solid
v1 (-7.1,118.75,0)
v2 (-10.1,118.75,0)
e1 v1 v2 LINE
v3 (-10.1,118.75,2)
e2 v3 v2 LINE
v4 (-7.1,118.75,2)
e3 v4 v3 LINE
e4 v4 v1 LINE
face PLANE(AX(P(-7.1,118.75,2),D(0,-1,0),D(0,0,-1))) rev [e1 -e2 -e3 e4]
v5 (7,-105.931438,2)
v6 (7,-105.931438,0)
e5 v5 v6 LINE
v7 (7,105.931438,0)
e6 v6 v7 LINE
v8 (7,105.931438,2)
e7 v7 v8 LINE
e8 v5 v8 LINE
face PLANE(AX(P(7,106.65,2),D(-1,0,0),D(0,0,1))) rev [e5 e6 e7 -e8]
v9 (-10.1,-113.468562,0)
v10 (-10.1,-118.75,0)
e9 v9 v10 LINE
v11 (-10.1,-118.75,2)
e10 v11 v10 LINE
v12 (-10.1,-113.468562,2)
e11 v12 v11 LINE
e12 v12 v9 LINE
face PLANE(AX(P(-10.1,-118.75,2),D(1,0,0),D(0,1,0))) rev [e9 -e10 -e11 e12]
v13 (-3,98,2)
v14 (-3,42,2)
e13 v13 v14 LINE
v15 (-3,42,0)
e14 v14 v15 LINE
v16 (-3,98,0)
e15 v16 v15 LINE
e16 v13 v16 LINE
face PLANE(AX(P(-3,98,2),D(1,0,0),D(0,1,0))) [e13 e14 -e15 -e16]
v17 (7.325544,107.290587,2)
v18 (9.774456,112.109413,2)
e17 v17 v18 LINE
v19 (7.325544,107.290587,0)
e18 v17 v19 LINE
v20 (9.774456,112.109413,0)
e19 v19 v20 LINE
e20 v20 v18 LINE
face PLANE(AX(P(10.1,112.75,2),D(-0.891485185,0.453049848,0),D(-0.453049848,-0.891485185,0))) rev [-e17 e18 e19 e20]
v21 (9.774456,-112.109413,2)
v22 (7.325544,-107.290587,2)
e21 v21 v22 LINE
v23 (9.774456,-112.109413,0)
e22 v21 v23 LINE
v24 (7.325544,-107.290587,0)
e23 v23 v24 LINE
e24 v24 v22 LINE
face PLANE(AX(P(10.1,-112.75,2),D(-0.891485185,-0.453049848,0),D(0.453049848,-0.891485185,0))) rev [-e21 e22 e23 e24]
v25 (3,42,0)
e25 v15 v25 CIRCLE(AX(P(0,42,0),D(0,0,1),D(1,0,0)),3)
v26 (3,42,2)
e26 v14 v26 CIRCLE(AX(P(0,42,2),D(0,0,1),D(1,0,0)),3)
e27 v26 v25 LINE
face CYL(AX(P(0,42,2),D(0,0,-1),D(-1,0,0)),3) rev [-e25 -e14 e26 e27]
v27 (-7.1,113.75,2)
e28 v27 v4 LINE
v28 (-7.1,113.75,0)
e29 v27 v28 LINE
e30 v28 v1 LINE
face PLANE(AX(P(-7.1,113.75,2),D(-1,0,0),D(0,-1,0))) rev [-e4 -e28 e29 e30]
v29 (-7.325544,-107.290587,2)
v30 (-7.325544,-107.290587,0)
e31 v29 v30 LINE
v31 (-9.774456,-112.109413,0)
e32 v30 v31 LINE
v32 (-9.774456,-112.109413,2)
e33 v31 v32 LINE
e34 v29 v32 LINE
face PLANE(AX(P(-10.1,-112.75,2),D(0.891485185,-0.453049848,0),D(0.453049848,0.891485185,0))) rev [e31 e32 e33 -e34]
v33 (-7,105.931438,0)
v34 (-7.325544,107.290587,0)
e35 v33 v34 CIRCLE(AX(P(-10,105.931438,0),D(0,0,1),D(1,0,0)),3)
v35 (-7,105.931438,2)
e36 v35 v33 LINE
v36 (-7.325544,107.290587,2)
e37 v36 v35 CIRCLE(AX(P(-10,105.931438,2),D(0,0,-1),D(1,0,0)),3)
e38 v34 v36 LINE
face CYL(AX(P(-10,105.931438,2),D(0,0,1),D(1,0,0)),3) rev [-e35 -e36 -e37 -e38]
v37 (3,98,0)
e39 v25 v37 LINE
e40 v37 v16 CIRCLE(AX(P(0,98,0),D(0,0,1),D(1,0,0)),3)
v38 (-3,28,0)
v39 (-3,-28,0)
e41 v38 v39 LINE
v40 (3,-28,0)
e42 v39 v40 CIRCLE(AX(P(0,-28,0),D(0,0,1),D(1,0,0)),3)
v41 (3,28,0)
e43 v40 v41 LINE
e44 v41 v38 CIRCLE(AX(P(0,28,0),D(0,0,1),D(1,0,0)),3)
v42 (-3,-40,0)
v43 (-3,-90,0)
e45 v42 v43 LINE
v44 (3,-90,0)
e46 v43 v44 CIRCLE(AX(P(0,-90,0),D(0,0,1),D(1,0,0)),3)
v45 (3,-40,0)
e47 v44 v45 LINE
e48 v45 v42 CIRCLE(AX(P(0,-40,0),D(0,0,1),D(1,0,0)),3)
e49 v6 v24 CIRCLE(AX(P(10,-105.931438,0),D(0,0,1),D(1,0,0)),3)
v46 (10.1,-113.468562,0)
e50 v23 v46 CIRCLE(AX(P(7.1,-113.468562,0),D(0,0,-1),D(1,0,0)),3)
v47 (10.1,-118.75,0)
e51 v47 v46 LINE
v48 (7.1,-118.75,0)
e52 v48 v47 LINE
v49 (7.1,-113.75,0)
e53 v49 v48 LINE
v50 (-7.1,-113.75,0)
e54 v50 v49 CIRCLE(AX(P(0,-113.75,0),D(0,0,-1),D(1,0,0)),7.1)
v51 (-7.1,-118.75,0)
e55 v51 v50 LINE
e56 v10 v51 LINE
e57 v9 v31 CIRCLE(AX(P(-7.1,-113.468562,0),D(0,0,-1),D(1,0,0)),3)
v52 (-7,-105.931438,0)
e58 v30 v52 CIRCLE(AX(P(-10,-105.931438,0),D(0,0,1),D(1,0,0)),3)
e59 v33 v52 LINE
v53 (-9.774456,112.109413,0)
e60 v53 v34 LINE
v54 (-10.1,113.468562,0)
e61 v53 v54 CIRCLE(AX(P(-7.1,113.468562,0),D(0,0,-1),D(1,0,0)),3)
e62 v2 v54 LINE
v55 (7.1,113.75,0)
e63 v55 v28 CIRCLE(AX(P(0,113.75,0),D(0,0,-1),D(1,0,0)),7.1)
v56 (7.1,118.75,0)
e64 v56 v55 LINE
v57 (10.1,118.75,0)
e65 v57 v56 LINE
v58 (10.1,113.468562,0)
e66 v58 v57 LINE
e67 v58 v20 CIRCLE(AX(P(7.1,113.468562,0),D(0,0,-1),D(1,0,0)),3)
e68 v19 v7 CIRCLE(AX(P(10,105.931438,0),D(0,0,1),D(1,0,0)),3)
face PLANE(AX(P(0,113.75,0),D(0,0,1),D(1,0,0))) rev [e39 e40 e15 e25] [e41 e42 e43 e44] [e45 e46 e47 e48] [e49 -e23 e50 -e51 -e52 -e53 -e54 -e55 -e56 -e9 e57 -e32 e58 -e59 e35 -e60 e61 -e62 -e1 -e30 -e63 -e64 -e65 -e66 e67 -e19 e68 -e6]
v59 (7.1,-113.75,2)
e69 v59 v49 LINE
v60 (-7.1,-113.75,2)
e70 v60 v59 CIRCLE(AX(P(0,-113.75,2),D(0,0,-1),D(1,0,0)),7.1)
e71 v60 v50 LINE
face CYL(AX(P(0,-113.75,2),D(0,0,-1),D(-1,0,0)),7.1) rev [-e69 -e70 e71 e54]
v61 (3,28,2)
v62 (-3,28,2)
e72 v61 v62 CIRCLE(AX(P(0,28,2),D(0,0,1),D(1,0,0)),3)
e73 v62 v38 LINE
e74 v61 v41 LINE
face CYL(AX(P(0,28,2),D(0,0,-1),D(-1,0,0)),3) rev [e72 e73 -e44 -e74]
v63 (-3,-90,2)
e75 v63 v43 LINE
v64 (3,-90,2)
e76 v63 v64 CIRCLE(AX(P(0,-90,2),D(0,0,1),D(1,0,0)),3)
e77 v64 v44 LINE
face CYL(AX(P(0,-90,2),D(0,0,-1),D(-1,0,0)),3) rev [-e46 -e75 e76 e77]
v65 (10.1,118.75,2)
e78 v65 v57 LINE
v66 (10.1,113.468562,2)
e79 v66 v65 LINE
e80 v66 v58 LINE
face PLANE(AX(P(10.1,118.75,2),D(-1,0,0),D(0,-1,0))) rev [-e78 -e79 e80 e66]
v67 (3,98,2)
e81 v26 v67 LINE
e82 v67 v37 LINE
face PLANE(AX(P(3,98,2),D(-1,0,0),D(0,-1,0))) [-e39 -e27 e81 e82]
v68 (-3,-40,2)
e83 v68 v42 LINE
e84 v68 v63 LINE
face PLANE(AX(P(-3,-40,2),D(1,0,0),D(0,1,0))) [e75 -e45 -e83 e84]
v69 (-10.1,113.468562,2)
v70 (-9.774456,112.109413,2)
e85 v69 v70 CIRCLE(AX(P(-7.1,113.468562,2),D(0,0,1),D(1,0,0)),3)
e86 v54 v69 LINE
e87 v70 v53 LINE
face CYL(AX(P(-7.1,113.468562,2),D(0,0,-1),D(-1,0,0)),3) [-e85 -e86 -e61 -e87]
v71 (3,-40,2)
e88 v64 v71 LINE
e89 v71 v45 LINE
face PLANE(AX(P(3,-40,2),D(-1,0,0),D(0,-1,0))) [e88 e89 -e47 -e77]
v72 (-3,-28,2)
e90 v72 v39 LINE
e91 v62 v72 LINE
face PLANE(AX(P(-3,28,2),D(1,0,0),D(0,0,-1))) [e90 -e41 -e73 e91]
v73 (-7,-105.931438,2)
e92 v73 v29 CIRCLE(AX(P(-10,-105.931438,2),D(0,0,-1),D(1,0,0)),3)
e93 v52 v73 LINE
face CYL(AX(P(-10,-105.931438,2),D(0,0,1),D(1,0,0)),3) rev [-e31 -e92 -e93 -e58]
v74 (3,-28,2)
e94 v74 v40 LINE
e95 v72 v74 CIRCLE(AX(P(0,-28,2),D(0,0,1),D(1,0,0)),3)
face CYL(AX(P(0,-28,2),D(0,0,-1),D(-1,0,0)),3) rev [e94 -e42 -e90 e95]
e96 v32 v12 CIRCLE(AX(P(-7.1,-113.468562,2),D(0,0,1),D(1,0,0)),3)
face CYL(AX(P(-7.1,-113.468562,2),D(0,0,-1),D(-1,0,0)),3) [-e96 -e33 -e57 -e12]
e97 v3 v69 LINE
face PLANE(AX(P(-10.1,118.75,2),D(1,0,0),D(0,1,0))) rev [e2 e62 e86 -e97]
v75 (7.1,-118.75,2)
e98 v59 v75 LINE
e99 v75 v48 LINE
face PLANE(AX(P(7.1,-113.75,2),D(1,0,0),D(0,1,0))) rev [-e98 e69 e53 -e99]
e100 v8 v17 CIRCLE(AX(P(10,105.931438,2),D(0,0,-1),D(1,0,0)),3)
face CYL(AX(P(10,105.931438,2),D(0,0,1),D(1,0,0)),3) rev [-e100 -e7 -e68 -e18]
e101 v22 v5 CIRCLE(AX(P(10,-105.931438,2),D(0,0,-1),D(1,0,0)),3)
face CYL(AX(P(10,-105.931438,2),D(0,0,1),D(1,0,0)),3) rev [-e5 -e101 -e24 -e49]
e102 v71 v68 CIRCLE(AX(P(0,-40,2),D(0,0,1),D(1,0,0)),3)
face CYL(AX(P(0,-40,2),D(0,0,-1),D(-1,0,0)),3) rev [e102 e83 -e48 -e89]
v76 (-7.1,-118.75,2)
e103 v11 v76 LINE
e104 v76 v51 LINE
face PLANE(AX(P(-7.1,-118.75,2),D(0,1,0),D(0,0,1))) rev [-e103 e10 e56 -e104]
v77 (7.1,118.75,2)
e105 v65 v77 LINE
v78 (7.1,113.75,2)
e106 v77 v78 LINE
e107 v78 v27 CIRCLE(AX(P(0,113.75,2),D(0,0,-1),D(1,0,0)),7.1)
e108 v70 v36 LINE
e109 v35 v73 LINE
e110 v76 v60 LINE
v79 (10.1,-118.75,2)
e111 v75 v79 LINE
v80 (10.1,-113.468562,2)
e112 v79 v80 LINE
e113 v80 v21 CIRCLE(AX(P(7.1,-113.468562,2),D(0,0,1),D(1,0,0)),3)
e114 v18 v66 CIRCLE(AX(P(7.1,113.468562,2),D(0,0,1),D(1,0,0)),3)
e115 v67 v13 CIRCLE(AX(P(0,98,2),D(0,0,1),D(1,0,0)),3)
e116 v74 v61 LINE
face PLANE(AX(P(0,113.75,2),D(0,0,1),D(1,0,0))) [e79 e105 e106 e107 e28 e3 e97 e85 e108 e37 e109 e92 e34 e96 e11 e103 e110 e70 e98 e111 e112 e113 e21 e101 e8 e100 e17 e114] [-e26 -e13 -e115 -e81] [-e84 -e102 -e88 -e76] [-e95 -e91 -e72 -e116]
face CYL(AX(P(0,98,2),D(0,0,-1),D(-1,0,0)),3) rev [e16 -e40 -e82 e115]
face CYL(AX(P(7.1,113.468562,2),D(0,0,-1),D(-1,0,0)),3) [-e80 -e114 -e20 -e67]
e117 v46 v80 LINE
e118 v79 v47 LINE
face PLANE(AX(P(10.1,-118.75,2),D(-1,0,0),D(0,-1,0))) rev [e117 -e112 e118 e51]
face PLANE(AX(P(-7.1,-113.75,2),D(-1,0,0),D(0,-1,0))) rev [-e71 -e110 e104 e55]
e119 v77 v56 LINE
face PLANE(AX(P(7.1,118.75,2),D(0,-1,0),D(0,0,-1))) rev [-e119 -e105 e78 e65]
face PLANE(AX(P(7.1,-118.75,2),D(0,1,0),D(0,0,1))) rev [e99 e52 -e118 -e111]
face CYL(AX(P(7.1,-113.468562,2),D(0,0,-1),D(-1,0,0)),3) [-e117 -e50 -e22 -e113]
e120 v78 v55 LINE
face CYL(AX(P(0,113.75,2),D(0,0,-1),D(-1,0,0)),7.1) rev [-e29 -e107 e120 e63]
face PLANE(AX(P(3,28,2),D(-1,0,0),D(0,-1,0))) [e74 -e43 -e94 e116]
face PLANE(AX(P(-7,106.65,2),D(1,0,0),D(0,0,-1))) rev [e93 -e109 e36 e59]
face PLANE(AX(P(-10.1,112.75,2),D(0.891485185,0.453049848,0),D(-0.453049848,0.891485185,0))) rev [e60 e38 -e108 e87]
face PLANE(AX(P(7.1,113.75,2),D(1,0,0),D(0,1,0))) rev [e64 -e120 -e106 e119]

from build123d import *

# Parameters (mm, degrees)
EXTRUDE_1_DEPTH = 2
FILLET_1_R      = 3


with BuildPart() as part:
    # 草图1 → 凸台-拉伸1 (new body)
    with BuildSketch(Plane.XY):
        with BuildLine():
            Line((-7, 106.65), (-7, -106.65))
            Line((-7, -106.65), (-10.1, -112.75))
            Line((-10.1, -112.75), (-10.1, -118.75))
            Line((-10.1, -118.75), (-7.1, -118.75))
            Line((-7.1, -118.75), (-7.1, -113.75))
            ThreePointArc((-7.1, -113.75), (0, -106.65), (7.1, -113.75))
            Line((7.1, -113.75), (7.1, -118.75))
            Line((7.1, -118.75), (10.1, -118.75))
            Line((10.1, -118.75), (10.1, -112.75))
            Line((10.1, -112.75), (7, -106.65))
            Line((7, -106.65), (7, 106.65))
            Line((7, 106.65), (10.1, 112.75))
            Line((10.1, 112.75), (10.1, 118.75))
            Line((10.1, 118.75), (7.1, 118.75))
            Line((7.1, 118.75), (7.1, 113.75))
            ThreePointArc((7.1, 113.75), (0, 106.65), (-7.1, 113.75))
            Line((-7.1, 113.75), (-7.1, 118.75))
            Line((-7.1, 118.75), (-10.1, 118.75))
            Line((-10.1, 118.75), (-10.1, 112.75))
            Line((-10.1, 112.75), (-7, 106.65))
        make_face()
        with BuildLine():
            Line((3, 98), (3, 42))
            ThreePointArc((3, 42), (0, 39), (-3, 42))
            Line((-3, 42), (-3, 98))
            ThreePointArc((-3, 98), (0, 101), (3, 98))
        make_face(mode=Mode.SUBTRACT)
        with BuildLine():
            Line((3, 28), (3, -28))
            ThreePointArc((3, -28), (0, -31), (-3, -28))
            Line((-3, -28), (-3, 28))
            ThreePointArc((-3, 28), (0, 31), (3, 28))
        make_face(mode=Mode.SUBTRACT)
        with BuildLine():
            Line((3, -40), (3, -90))
            ThreePointArc((3, -90), (0, -93), (-3, -90))
            Line((-3, -90), (-3, -40))
            ThreePointArc((-3, -40), (0, -37), (3, -40))
        make_face(mode=Mode.SUBTRACT)
    extrude(amount=EXTRUDE_1_DEPTH)

    # 圆角1
    fillet_1_edges = [part.edges().sort_by_distance(p)[0] for p in [
        (10.1, 112.75, 1),
        (7, 106.65, 1),
        (7, -106.65, 1),
        (10.1, -112.75, 1),
        (-10.1, -112.75, 1),
        (-7, -106.65, 1),
        (-7, 106.65, 1),
        (-10.1, 112.75, 1),
    ]]
    fillet(fillet_1_edges, radius=FILLET_1_R)


solid = part.part
